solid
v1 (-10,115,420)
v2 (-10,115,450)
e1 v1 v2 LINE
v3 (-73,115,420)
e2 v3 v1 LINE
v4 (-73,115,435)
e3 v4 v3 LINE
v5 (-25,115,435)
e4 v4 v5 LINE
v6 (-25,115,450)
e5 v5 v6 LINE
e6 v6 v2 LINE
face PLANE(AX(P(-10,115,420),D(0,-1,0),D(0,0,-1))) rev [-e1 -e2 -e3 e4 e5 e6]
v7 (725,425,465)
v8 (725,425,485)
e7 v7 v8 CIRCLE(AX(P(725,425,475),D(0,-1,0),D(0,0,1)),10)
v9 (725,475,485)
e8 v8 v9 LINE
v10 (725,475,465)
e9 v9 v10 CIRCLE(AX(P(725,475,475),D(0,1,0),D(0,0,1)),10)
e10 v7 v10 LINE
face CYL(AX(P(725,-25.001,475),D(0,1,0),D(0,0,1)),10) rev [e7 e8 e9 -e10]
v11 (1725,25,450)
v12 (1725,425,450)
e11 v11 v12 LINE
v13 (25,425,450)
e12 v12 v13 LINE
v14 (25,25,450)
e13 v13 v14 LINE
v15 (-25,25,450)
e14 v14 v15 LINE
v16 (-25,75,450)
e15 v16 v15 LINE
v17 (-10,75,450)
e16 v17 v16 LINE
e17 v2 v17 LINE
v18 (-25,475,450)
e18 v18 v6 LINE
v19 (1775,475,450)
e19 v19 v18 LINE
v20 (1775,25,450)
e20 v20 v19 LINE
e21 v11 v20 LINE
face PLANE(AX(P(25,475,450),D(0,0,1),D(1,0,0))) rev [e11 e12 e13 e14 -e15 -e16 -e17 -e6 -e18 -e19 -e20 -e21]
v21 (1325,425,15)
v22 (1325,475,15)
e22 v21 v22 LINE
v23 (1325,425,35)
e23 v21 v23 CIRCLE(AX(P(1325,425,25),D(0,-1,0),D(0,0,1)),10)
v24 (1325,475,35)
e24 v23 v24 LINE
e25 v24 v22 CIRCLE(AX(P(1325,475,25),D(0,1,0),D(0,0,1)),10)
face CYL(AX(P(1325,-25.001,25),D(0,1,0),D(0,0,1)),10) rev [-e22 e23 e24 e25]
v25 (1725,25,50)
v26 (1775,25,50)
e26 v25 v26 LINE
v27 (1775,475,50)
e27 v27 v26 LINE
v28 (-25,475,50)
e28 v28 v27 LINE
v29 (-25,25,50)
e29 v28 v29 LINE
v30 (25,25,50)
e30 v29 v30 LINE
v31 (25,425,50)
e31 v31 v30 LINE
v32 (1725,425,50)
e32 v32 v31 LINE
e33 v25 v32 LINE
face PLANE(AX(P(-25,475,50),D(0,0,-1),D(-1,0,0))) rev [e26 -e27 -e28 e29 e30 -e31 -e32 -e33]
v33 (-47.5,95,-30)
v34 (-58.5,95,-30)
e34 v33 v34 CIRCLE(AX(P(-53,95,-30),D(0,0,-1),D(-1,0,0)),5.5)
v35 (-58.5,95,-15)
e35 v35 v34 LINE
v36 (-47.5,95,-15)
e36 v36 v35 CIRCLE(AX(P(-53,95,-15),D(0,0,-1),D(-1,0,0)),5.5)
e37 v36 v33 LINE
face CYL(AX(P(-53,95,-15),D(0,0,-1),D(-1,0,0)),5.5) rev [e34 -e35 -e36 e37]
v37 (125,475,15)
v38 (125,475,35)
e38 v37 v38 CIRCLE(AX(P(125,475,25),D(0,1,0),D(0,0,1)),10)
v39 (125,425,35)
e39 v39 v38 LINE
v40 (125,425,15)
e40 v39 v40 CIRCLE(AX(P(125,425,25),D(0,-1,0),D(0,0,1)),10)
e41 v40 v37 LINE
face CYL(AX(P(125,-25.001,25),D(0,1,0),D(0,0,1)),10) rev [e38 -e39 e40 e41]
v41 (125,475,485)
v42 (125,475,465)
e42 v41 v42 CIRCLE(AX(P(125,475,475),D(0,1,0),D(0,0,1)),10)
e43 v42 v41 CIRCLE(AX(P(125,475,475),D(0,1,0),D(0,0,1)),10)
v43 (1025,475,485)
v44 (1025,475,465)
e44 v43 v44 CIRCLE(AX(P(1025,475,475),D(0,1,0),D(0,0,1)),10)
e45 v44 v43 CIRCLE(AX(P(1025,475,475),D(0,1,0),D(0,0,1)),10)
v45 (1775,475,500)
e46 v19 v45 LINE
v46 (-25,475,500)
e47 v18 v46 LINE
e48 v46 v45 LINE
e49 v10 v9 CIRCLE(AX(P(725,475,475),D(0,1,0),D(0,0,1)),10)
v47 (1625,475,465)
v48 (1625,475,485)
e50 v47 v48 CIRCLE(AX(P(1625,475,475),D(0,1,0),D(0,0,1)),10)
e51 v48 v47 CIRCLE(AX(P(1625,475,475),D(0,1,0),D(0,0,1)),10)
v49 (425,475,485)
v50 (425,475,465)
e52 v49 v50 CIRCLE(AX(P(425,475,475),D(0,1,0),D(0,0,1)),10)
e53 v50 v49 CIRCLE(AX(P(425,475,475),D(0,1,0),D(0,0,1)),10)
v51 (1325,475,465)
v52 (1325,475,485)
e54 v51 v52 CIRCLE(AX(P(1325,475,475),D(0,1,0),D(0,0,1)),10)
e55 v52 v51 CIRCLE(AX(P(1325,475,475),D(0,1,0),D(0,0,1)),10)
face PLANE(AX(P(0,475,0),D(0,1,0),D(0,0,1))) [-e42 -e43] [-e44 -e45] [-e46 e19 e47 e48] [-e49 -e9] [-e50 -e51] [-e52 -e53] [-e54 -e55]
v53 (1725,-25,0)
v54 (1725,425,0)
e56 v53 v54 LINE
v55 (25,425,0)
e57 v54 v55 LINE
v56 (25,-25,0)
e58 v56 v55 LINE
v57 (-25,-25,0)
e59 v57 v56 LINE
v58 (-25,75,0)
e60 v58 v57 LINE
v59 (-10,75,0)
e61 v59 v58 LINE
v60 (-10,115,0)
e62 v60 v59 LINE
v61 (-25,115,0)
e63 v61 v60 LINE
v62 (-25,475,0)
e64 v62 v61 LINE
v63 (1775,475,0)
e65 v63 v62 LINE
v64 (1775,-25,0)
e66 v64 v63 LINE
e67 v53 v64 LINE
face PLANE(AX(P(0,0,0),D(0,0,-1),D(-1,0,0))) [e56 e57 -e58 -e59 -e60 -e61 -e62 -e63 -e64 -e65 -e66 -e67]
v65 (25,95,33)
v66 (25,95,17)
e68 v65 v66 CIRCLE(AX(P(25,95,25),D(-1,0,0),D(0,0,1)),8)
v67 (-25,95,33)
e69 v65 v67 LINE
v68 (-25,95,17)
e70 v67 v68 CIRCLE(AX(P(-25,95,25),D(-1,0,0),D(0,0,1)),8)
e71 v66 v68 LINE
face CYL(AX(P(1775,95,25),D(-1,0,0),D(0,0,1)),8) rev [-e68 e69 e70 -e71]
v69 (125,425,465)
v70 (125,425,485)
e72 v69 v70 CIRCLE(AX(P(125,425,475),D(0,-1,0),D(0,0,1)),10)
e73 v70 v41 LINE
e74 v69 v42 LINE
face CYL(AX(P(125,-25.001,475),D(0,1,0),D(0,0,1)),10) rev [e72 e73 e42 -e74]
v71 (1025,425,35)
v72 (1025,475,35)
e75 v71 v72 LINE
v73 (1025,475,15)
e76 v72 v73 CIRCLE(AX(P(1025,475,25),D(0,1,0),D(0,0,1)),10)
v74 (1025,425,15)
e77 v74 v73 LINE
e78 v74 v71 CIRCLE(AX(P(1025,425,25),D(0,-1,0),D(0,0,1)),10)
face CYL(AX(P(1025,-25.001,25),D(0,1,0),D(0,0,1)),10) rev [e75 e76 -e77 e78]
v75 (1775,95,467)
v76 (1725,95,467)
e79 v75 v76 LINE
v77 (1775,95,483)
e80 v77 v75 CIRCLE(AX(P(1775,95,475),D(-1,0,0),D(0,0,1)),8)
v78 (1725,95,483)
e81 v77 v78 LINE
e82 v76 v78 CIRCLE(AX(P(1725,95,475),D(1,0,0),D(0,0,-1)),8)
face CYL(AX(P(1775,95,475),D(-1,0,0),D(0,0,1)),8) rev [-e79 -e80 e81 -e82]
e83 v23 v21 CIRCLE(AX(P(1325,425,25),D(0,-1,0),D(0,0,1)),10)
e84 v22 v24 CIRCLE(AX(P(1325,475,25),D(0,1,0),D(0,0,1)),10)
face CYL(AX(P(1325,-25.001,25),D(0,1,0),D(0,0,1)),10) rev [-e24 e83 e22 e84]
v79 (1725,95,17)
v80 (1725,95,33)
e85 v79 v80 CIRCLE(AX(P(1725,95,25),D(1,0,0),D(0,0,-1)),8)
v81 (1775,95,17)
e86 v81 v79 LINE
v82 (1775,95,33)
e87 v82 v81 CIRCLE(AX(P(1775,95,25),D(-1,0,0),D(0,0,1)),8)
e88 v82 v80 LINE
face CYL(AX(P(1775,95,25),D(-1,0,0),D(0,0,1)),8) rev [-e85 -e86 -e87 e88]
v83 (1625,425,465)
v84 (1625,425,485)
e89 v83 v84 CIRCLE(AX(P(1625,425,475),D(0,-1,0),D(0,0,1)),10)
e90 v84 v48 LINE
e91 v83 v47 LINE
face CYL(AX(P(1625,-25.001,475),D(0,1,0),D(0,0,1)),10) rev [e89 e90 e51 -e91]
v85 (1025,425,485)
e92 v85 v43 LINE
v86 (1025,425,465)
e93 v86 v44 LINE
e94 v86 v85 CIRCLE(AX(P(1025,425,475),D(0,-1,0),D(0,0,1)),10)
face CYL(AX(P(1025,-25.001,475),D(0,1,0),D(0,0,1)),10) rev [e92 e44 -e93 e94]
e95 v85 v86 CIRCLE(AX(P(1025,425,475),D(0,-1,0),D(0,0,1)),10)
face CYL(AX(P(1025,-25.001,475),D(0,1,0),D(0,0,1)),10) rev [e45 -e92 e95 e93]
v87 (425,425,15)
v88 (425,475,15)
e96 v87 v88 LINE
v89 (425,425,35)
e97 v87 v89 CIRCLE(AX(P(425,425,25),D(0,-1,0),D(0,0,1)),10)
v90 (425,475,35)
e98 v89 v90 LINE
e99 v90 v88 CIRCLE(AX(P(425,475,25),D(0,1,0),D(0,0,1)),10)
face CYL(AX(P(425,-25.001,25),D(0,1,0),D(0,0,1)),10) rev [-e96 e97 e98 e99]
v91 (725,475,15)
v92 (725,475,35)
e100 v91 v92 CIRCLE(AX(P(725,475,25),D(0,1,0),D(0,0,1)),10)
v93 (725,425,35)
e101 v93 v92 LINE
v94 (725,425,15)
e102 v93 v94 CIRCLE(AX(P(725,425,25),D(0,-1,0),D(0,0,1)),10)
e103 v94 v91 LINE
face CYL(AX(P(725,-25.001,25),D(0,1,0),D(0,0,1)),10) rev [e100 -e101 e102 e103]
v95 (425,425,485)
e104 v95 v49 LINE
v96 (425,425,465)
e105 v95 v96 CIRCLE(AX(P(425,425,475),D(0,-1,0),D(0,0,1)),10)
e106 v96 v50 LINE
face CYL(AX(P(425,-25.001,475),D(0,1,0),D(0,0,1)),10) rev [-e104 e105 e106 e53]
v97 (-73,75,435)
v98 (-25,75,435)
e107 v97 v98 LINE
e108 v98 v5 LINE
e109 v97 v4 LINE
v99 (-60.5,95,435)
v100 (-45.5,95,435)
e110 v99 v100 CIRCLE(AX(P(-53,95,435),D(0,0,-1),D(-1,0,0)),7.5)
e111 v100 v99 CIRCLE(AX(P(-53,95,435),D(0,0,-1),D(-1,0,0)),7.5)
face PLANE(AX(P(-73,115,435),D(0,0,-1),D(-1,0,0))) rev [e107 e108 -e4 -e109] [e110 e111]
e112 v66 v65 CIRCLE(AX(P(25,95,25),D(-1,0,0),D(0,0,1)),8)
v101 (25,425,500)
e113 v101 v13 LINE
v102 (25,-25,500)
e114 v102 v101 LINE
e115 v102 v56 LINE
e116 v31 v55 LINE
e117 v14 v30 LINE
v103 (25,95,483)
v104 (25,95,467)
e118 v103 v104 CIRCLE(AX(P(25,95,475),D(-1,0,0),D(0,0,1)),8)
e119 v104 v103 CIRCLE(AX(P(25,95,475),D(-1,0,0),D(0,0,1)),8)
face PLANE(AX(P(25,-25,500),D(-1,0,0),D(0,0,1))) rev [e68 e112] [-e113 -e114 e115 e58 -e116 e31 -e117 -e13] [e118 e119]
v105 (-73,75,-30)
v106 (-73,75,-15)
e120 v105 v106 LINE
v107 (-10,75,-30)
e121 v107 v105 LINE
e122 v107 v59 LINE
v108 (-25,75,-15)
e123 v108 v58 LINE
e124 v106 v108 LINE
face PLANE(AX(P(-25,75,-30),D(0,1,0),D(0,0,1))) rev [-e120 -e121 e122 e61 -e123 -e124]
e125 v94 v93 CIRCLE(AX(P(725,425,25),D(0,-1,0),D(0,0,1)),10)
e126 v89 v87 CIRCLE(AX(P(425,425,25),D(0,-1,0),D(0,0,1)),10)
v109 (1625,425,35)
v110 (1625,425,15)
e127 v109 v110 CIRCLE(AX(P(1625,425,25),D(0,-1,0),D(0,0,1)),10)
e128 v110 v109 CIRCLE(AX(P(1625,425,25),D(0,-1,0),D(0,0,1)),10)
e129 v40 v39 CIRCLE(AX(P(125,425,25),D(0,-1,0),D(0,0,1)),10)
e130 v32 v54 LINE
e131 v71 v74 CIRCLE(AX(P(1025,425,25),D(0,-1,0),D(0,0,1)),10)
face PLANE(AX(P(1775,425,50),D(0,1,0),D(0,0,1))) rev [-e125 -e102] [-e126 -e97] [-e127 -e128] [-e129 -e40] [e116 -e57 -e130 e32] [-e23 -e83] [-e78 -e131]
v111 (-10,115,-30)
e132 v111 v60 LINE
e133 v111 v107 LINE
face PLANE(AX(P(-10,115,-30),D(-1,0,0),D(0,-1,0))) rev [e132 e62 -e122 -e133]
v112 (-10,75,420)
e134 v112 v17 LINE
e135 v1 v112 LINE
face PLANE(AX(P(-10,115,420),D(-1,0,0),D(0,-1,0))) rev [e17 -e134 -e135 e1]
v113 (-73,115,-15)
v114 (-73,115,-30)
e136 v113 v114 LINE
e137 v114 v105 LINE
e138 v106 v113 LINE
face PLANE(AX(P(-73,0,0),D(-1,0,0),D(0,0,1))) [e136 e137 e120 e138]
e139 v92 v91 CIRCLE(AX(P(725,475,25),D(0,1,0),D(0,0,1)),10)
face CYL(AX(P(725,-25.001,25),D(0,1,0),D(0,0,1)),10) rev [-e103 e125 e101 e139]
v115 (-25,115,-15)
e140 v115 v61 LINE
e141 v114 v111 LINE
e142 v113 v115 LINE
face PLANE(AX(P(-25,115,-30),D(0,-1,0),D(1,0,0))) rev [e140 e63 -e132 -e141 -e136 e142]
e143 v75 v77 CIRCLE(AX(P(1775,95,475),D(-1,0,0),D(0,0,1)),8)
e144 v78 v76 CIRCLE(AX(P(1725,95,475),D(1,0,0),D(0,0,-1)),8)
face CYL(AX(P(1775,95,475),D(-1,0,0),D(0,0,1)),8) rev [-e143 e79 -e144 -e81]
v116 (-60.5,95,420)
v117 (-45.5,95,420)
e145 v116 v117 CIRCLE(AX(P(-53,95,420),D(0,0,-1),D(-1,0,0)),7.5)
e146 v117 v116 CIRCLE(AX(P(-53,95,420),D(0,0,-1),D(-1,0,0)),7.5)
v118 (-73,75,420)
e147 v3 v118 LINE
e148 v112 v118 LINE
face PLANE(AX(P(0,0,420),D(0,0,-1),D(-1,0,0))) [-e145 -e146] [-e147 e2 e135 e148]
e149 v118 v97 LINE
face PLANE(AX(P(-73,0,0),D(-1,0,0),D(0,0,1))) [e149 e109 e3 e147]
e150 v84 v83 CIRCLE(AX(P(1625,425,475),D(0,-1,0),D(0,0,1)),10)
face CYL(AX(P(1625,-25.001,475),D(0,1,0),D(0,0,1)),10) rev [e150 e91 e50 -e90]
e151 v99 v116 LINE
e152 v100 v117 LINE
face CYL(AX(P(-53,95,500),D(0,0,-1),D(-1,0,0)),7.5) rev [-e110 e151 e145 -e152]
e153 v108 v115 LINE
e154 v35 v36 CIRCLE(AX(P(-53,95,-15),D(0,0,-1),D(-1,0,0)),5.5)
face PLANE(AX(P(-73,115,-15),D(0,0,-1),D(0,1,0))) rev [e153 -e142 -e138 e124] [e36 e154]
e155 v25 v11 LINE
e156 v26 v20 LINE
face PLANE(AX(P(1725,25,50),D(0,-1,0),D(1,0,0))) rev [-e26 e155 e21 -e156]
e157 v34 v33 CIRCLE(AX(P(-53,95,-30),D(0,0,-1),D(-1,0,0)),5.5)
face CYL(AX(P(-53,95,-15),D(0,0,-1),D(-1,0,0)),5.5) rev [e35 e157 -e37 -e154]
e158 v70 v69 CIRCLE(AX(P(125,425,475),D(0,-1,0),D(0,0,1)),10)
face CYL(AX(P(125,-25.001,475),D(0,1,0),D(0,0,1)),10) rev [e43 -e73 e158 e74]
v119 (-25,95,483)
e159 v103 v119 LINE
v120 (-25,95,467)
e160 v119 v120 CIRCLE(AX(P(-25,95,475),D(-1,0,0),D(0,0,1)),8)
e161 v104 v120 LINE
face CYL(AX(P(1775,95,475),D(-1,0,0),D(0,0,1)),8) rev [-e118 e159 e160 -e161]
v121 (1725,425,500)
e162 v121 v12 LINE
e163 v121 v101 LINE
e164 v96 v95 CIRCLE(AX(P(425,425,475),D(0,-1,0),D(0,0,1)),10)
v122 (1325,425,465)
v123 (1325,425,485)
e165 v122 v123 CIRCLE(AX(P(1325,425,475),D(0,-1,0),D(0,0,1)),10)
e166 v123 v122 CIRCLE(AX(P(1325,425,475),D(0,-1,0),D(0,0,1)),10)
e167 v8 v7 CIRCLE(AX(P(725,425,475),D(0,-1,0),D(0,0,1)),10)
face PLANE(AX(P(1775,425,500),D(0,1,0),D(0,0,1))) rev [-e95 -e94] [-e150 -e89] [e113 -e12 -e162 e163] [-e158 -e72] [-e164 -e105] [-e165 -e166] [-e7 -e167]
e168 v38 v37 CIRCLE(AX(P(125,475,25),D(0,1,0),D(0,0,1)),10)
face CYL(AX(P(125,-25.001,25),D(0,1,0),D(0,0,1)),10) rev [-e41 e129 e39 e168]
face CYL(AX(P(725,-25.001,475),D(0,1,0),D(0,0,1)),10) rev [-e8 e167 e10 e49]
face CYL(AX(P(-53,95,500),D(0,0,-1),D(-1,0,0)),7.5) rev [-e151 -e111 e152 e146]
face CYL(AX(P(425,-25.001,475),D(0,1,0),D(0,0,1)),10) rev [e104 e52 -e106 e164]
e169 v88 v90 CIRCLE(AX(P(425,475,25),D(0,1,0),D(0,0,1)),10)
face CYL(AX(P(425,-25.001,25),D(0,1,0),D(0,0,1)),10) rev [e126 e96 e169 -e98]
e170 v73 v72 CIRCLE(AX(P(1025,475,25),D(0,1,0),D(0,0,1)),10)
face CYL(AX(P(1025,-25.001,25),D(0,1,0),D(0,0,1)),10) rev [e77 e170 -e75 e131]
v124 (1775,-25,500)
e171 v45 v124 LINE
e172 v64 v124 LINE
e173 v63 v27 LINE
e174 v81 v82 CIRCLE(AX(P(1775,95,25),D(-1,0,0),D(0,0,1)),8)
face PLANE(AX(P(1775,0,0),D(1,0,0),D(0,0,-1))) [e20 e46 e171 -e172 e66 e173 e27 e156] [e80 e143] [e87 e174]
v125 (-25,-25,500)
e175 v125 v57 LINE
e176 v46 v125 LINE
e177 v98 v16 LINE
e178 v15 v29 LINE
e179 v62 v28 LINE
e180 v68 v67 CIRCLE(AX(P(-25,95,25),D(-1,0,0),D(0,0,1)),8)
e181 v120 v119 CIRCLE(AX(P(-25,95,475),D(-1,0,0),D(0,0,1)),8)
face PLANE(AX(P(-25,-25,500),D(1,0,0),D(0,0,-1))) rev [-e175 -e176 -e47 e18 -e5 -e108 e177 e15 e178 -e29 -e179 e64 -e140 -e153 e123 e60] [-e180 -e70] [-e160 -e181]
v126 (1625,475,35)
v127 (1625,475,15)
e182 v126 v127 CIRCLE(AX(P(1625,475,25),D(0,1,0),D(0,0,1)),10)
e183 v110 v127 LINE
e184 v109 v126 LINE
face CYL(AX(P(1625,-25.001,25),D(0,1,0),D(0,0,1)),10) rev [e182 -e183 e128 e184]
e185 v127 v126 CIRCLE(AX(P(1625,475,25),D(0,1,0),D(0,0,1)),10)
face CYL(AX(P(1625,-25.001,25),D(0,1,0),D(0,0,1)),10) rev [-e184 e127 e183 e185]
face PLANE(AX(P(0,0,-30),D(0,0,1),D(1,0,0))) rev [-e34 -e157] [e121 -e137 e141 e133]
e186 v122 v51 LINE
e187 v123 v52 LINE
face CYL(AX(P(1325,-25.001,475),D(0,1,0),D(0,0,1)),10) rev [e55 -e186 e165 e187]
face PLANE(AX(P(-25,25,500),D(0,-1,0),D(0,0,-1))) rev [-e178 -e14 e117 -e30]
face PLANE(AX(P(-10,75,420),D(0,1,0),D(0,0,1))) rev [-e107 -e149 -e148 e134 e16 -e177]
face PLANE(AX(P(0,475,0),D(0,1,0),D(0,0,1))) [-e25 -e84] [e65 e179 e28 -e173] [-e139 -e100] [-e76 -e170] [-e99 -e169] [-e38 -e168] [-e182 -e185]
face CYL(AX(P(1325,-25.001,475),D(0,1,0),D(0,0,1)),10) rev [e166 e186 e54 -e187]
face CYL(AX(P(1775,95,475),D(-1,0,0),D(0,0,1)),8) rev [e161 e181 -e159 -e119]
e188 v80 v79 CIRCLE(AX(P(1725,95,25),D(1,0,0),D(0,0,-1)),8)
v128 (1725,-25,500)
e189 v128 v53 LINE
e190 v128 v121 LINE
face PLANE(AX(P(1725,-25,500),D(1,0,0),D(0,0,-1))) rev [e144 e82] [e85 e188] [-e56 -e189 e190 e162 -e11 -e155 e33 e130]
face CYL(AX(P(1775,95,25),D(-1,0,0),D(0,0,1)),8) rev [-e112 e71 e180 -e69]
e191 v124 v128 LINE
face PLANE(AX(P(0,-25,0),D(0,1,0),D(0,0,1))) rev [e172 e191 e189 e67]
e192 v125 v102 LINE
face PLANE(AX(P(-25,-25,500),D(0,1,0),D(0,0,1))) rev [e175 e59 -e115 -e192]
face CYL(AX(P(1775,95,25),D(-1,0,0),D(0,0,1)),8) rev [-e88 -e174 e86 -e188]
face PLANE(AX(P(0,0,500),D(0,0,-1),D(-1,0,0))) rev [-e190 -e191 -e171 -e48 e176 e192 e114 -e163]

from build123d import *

# Parameters (mm, degrees)
SKETCH1_W               = 50
SKETCH1_H               = 50
BOSS_EXTRUDE1_DEPTH     = 500
SKETCH2_W               = 50
SKETCH2_H               = 50
BOSS_EXTRUDE2_DEPTH     = 450
SKETCH3_W               = 50
SKETCH3_H               = 50
BOSS_EXTRUDE3_DEPTH     = 1750
SKETCH4_W               = 50
SKETCH4_H               = 50
BOSS_EXTRUDE4_DEPTH     = 450
SKETCH5_W               = 50
SKETCH5_H               = 50
BOSS_EXTRUDE5_DEPTH     = 400
CUT_EXTRUDE1_REACH      = 1912.661
SKETCH6_R               = 10
LPATTERN1_COUNT         = 6
LPATTERN1_PITCH         = 300
SKETCH8_R               = 8
CUT_EXTRUDE2_DEPTH      = 1928.59565262
SKETCH9_W               = 15
SKETCH9_H               = 40
BOSS_EXTRUDE6_DEPTH     = 30
SKETCH12_W              = 15
SKETCH12_H              = 40
BOSS_EXTRUDE7_DEPTH     = 30
SKETCH13_W              = 15
SKETCH13_H              = 40
BOSS_EXTRUDE8_DEPTH     = 48
CUT_EXTRUDE3_DEPTH      = 1913.367642479
CUT_EXTRUDE3_DEPTH_BACK = 1913.367642479
SKETCH14_R              = 7.5
SKETCH15_R              = 7.5
SKETCH15_R_2            = 5.5
BOSS_EXTRUDE9_DEPTH     = 15


with BuildPart() as part:
    # Sketch1 → Boss-Extrude1 (new body)
    with BuildSketch(Plane.XY):
        Rectangle(SKETCH1_W, SKETCH1_H)
    extrude(amount=BOSS_EXTRUDE1_DEPTH)

    # Sketch2 → Boss-Extrude2 (add)
    with BuildSketch(Plane(origin=(0, 25, 0), x_dir=(1, 0, 0), z_dir=(0, 1, 0))):
        with Locations((0, -25)):
            Rectangle(SKETCH2_W, SKETCH2_H)
        with Locations((0, -475)):
            Rectangle(SKETCH2_W, SKETCH2_H)
    extrude(amount=BOSS_EXTRUDE2_DEPTH)

    # Sketch3 → Boss-Extrude3 (add)
    with BuildSketch(Plane(origin=(25, 0, 0), x_dir=(0, 0, -1), z_dir=(1, 0, 0))):
        with Locations((-475, 450)):
            Rectangle(SKETCH3_W, SKETCH3_H)
        with Locations((-25, 450)):
            Rectangle(SKETCH3_W, SKETCH3_H)
    extrude(amount=BOSS_EXTRUDE3_DEPTH)

    # Sketch4 → Boss-Extrude4 (add)
    with BuildSketch(Plane(origin=(0, 425, 0), x_dir=(-1, 0, 0), z_dir=(0, -1, 0))):
        with Locations((-1750, -475)):
            Rectangle(SKETCH4_W, SKETCH4_H)
        with Locations((-1750, -25)):
            Rectangle(SKETCH4_W, SKETCH4_H)
    extrude(amount=BOSS_EXTRUDE4_DEPTH)

    # Sketch5 → Boss-Extrude5 (add)
    with BuildSketch(Plane(origin=(0, 0, 450), x_dir=(-1, 0, 0), z_dir=(0, 0, -1))):
        with Locations((-1750, 0)):
            Rectangle(SKETCH5_W, SKETCH5_H)
    extrude(amount=BOSS_EXTRUDE5_DEPTH)

    # Sketch6 → Cut-Extrude1 (cut, up to next)
    with BuildSketch(Plane(origin=(0, 475, 0), x_dir=(1, 0, 0), z_dir=(0, 1, 0)), mode=Mode.PRIVATE) as cut_extrude1_sk1:
        with Locations(Location((125, -25, 0), (0, 0, 270))):
            Circle(SKETCH6_R)
    cut_extrude1_tool1 = extrude(cut_extrude1_sk1.sketch, amount=-CUT_EXTRUDE1_REACH, mode=Mode.PRIVATE) & part.part
    # Sketch6 → Cut-Extrude1 (cut, up to next)
    with BuildSketch(Plane(origin=(0, 475, 0), x_dir=(1, 0, 0), z_dir=(0, 1, 0)), mode=Mode.PRIVATE) as cut_extrude1_sk2:
        with Locations(Location((125, -475, 0), (0, 0, 270))):
            Circle(SKETCH6_R)
    cut_extrude1_tool2 = extrude(cut_extrude1_sk2.sketch, amount=-CUT_EXTRUDE1_REACH, mode=Mode.PRIVATE) & part.part
    cut_extrude1_1 = cut_extrude1_tool1.solids().sort_by_distance((125, 475, 25))[0]
    add(cut_extrude1_1, mode=Mode.SUBTRACT)
    cut_extrude1_2 = cut_extrude1_tool2.solids().sort_by_distance((125, 475, 475))[0]
    add(cut_extrude1_2, mode=Mode.SUBTRACT)
    cut_extrude1 = cut_extrude1_1 + cut_extrude1_2  # Cut-Extrude1 as one shape, for the pattern or mirror that repeats it

    # LPattern1: Cut-Extrude1 ×6
    with Locations(*[(i * LPATTERN1_PITCH, 0, 0) for i in range(1, LPATTERN1_COUNT)]):
        add(cut_extrude1, mode=Mode.SUBTRACT)

    # Sketch8 → Cut-Extrude2 (cut, through all)
    with BuildSketch(Plane.ZY.offset(25)):
        with Locations((475, 95)):
            Circle(SKETCH8_R)
        with Locations((25, 95)):
            Circle(SKETCH8_R)
    extrude(amount=-CUT_EXTRUDE2_DEPTH, mode=Mode.SUBTRACT)

    # Sketch9 → Boss-Extrude6 (add)
    with BuildSketch(Plane(origin=(0, 0, 450), x_dir=(-1, 0, 0), z_dir=(0, 0, -1))):
        with Locations((17.5, 95)):
            Rectangle(SKETCH9_W, SKETCH9_H)
    extrude(amount=BOSS_EXTRUDE6_DEPTH)

    # Sketch12 → Boss-Extrude7 (add)
    with BuildSketch(Plane(origin=(0, 0, 0), x_dir=(-1, 0, 0), z_dir=(0, 0, -1))):
        with Locations((17.5, 95)):
            Rectangle(SKETCH12_W, SKETCH12_H)
    extrude(amount=BOSS_EXTRUDE7_DEPTH)

    # Sketch13 → Boss-Extrude8 (add)
    with BuildSketch(Plane.ZY.offset(25)):
        with Locations((-22.5, 95)):
            Rectangle(SKETCH13_W, SKETCH13_H)
        with Locations((427.5, 95)):
            Rectangle(SKETCH13_W, SKETCH13_H)
    extrude(amount=BOSS_EXTRUDE8_DEPTH)

    # Sketch14 → Cut-Extrude3 (cut, two sides: drawn at the far end of the back side and taken through both)
    with BuildSketch(Plane(origin=(0, 0, -30), x_dir=(-1, 0, 0), z_dir=(0, 0, -1)).offset(-CUT_EXTRUDE3_DEPTH_BACK)):
        with Locations(Location((53, 95, 0), (0, 0, 90))):
            Circle(SKETCH14_R)
    extrude(amount=CUT_EXTRUDE3_DEPTH + CUT_EXTRUDE3_DEPTH_BACK, mode=Mode.SUBTRACT)

    # Sketch15 → Boss-Extrude9 (add)
    with BuildSketch(Plane(origin=(0, 0, -30), x_dir=(-1, 0, 0), z_dir=(0, 0, -1))):
        with Locations((53, 95)):
            Circle(SKETCH15_R)
        with Locations((53, 95)):
            Circle(SKETCH15_R_2, mode=Mode.SUBTRACT)
    extrude(amount=-BOSS_EXTRUDE9_DEPTH)


solid = part.part
